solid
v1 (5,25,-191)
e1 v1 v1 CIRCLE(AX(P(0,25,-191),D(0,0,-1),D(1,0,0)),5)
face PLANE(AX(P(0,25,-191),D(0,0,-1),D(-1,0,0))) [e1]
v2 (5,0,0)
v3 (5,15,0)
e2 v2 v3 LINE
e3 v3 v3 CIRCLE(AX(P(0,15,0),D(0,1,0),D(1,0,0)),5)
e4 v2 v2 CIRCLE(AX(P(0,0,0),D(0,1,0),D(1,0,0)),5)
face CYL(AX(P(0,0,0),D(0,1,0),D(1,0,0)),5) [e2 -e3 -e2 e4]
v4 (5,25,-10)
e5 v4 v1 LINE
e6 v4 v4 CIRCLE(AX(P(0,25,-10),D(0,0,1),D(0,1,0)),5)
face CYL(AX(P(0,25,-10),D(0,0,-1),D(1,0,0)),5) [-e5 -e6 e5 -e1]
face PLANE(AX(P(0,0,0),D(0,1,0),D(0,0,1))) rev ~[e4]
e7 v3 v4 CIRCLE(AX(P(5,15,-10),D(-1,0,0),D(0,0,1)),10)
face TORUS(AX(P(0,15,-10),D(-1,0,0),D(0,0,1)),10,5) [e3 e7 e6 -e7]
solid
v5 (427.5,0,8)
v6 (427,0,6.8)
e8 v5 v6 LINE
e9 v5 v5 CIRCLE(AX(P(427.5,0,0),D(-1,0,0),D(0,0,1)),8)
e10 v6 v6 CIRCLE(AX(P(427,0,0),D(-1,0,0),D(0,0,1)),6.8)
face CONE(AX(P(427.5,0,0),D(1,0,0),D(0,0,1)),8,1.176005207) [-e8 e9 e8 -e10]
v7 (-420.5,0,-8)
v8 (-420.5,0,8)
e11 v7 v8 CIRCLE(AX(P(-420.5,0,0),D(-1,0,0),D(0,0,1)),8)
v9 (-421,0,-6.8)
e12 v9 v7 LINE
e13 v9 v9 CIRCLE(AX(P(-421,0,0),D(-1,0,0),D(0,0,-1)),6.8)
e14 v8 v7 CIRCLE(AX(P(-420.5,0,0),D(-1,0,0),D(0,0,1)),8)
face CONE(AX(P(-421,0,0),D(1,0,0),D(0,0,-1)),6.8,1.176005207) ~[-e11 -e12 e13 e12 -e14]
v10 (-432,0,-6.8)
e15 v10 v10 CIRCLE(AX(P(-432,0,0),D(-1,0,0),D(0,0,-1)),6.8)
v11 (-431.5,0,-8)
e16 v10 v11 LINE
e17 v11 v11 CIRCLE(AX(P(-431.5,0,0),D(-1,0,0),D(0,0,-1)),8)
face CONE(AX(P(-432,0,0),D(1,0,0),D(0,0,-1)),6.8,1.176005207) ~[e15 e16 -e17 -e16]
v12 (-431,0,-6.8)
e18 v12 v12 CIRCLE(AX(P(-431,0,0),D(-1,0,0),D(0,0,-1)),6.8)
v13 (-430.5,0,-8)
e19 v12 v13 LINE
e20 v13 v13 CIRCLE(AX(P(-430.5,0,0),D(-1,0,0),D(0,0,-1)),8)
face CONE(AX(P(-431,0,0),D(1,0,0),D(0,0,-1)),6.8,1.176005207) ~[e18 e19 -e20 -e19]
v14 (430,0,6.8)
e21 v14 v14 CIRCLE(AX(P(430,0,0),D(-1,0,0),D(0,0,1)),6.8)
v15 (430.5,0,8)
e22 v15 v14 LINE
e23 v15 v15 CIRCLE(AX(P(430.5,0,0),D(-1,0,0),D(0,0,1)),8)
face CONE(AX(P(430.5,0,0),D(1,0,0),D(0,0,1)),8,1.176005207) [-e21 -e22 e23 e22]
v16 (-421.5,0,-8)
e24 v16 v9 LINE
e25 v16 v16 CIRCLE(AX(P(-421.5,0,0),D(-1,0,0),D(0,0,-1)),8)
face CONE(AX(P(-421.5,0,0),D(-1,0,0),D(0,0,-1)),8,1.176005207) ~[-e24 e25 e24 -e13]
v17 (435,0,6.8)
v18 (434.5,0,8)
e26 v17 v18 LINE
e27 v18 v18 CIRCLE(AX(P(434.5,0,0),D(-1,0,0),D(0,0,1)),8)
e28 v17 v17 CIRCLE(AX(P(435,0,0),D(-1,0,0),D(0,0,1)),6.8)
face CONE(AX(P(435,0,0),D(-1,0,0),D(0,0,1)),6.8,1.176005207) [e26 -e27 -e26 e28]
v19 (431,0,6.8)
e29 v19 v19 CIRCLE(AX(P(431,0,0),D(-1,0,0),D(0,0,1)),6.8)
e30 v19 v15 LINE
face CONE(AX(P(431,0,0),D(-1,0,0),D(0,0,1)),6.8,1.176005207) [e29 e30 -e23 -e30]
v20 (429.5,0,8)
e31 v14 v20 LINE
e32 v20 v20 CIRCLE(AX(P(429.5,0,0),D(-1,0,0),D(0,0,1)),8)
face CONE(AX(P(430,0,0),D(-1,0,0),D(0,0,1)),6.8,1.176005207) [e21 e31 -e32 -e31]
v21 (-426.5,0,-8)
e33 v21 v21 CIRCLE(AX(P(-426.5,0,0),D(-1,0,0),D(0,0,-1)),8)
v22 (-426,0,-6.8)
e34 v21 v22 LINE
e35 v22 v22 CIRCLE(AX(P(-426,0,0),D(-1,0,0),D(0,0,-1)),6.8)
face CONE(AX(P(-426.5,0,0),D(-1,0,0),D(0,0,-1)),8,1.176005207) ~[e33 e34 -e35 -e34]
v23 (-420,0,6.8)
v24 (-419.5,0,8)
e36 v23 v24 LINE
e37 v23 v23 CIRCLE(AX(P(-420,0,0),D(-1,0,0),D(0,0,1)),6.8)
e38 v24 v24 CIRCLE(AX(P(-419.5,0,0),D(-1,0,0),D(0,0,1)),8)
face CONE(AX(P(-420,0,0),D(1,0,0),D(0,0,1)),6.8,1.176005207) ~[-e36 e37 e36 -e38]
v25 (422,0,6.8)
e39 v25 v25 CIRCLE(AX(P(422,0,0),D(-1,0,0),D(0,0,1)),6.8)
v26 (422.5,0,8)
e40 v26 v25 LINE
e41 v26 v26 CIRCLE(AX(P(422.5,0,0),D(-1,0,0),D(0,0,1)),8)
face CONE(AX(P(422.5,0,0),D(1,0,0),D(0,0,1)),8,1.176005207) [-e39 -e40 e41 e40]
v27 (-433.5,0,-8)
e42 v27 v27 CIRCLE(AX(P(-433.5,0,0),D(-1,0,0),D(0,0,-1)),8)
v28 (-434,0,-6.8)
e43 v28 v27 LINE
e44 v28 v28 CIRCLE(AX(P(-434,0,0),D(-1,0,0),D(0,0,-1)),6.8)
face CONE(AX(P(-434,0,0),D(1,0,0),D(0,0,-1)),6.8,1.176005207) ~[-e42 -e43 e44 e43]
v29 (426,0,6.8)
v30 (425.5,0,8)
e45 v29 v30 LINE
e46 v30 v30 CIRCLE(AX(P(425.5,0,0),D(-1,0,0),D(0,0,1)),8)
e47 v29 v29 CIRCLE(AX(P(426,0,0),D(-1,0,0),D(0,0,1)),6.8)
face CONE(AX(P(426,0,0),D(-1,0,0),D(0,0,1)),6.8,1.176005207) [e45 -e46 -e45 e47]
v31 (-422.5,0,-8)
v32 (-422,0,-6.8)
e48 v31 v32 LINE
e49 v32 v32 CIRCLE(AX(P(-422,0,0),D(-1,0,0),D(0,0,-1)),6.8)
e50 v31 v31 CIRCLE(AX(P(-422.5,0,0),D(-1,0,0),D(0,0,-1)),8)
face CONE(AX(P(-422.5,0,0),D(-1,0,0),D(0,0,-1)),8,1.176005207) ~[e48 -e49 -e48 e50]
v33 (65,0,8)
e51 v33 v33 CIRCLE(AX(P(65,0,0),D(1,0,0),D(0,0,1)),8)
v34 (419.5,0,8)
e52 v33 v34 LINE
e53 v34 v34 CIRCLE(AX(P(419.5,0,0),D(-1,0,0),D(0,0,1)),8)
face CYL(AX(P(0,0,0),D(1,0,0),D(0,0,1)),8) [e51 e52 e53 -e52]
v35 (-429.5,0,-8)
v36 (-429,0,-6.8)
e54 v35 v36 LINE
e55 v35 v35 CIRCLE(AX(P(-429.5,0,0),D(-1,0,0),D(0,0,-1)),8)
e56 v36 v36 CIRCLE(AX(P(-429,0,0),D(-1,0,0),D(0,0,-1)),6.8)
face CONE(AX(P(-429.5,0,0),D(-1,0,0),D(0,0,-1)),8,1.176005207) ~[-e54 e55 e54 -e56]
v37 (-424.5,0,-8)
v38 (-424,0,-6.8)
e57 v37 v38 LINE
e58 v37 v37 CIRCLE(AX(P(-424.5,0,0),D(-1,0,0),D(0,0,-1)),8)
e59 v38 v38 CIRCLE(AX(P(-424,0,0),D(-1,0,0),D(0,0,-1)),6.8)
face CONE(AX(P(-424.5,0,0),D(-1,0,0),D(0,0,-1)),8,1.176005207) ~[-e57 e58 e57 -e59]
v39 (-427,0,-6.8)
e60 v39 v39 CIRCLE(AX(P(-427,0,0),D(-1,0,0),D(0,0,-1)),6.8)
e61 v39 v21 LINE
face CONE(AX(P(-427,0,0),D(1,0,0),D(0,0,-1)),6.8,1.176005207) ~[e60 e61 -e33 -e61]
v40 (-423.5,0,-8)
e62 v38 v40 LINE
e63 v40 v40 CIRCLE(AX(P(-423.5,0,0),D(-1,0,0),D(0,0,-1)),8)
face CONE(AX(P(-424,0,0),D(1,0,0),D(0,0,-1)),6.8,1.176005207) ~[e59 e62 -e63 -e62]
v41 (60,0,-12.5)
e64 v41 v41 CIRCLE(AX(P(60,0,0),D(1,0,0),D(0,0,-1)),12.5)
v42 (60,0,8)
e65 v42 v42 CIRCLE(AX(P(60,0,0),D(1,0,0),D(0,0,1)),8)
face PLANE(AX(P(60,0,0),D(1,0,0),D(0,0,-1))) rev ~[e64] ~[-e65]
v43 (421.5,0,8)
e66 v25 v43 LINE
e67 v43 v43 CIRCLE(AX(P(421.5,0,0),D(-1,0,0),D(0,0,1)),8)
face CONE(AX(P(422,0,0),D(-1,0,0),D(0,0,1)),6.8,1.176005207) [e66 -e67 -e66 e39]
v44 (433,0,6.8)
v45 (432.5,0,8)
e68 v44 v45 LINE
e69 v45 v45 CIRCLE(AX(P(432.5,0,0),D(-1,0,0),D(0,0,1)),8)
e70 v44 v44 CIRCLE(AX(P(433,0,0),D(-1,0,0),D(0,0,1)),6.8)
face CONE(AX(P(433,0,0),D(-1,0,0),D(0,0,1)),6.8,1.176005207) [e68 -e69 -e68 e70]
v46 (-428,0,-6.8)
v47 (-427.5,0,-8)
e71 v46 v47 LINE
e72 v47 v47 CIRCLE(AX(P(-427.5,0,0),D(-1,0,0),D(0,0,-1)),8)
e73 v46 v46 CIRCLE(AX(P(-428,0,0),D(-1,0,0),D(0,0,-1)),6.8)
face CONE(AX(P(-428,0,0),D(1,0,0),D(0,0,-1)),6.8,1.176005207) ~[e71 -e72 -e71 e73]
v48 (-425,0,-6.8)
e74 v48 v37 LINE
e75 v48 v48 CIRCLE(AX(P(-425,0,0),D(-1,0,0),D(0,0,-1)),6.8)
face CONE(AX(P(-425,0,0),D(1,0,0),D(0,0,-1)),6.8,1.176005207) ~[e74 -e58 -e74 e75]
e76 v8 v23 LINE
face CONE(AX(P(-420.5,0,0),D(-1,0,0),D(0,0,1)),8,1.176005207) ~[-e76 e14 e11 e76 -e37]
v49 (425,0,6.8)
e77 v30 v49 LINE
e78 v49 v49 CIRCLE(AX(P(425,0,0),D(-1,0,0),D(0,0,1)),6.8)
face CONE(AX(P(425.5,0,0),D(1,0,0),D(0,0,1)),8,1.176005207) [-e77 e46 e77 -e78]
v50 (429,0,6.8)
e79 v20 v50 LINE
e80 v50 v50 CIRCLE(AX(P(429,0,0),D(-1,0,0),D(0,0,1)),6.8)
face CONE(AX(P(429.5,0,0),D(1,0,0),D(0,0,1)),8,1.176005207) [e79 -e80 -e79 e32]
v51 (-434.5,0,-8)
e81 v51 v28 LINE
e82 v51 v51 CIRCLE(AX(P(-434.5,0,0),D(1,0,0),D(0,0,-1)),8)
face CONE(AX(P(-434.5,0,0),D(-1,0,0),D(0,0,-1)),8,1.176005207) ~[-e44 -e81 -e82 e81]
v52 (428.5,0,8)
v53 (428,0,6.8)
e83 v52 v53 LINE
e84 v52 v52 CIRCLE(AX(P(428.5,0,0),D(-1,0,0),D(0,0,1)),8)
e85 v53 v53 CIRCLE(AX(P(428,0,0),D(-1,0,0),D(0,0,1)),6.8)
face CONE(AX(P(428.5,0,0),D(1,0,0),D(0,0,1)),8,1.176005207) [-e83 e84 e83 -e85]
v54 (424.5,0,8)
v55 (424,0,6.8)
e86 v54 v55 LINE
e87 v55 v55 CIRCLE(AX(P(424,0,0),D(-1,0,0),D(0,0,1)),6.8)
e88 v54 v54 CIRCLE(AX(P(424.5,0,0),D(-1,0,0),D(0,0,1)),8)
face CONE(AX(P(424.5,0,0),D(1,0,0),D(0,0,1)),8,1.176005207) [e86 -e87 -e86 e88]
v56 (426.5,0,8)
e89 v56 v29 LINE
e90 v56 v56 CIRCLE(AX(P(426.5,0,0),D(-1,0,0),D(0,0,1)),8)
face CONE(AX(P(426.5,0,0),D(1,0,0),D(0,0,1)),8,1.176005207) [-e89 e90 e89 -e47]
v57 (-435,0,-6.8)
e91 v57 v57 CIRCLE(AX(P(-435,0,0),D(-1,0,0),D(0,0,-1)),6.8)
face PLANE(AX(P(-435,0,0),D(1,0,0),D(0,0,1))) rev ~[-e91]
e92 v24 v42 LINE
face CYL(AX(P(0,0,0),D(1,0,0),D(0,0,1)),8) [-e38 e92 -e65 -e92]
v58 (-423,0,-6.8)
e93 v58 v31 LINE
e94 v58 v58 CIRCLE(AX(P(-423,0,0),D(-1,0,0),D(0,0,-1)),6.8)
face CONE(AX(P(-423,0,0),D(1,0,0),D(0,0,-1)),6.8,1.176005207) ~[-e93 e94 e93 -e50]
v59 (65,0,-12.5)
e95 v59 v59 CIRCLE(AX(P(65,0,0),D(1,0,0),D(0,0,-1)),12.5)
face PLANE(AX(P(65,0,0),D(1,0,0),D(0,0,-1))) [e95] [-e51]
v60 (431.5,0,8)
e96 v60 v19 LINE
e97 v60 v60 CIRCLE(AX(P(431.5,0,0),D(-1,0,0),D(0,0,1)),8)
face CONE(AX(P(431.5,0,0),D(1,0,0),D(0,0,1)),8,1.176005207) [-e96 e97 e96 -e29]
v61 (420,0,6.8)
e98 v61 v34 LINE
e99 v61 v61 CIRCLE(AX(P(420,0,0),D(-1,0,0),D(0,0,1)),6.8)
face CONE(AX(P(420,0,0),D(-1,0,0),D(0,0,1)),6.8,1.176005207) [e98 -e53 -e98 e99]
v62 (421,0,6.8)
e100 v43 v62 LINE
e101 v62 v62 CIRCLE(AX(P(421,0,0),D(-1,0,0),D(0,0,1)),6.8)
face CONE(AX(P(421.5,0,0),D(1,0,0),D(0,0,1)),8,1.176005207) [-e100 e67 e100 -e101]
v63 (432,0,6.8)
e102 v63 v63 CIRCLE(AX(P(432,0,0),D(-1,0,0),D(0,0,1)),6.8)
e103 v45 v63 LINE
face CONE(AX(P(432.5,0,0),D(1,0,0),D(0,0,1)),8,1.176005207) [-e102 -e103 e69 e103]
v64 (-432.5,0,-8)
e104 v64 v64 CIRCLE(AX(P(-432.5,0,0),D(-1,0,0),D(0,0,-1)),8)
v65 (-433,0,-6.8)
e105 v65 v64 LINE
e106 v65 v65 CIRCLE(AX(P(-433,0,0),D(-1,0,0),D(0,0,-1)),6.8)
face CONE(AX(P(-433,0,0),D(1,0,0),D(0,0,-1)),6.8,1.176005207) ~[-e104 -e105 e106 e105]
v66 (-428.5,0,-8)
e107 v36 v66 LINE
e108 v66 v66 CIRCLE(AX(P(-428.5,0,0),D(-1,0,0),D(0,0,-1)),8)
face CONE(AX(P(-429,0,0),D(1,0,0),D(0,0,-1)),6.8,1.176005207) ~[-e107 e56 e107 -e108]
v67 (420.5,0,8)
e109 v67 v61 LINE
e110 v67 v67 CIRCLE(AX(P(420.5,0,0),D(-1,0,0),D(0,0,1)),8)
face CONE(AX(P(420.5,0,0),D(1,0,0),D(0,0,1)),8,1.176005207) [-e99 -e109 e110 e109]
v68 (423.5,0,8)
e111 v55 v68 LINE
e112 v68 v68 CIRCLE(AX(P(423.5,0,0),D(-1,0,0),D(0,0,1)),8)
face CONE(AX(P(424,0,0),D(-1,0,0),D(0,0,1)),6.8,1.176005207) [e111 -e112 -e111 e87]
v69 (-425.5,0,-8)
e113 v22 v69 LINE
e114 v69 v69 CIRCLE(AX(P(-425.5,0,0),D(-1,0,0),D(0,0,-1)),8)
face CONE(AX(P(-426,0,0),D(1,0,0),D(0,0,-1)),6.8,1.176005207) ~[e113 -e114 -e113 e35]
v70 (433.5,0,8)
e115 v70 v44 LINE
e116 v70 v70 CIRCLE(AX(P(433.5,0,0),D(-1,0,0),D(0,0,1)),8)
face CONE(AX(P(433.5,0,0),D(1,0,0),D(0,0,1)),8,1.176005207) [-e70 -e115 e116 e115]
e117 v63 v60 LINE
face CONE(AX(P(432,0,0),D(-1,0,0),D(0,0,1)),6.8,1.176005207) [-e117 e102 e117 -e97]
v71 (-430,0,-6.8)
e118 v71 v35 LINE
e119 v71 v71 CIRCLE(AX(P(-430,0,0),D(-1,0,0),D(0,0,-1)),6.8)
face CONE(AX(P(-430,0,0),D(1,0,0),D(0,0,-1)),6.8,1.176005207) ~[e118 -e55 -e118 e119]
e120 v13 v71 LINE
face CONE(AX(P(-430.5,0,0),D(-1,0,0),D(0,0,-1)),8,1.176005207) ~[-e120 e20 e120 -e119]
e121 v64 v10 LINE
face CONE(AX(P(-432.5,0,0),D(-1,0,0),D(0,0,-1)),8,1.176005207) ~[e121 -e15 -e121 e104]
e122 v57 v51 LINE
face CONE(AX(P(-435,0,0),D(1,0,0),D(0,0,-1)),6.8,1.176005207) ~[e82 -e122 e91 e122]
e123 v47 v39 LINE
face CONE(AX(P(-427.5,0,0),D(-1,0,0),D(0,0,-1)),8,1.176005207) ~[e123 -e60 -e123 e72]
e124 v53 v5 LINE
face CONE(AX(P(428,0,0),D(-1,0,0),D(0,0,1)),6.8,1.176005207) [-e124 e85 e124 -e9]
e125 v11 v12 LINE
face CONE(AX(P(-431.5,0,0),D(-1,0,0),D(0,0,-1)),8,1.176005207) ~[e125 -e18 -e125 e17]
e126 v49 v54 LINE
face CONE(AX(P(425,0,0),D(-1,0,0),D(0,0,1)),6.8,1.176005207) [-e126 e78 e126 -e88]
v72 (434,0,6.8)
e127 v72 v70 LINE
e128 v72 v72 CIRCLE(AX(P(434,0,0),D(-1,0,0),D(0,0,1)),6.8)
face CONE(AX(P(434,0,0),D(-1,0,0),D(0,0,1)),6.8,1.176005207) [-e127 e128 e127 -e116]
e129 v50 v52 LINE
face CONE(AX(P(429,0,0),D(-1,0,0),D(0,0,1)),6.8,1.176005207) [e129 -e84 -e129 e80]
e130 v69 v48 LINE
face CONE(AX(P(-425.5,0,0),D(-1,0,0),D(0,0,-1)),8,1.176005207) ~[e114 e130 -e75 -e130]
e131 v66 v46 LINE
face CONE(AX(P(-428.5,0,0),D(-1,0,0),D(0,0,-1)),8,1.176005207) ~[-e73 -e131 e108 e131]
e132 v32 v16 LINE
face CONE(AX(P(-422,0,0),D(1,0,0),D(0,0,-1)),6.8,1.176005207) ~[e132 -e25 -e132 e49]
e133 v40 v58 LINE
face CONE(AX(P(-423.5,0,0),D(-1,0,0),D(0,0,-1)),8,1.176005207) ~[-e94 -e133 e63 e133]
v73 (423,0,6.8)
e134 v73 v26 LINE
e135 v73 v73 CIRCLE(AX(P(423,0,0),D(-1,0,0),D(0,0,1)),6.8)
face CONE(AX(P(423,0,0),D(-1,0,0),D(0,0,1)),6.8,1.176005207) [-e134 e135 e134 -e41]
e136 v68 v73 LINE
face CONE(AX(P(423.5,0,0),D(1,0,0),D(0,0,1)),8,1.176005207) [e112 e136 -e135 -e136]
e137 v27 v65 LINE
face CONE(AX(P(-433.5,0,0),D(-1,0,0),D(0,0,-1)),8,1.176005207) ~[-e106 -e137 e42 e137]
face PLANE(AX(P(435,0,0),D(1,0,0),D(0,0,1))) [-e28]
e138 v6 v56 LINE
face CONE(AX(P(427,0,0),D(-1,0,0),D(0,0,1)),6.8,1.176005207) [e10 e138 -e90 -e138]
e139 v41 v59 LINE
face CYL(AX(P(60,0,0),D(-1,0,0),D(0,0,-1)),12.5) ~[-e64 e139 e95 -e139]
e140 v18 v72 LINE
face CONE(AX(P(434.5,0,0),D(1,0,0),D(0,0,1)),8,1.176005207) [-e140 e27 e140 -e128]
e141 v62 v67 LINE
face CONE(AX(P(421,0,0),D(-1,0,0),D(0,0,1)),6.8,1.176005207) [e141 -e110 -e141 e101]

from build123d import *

# Parameters (mm, degrees)
SKETCH_3_R             = 5
SKETCH_4_R             = 8
EXTRUDE_2_DEPTH        = 435
PATTERN_LINEAR_1_COUNT = 16
PATTERN_LINEAR_1_PITCH = 1
SKETCH_8_R             = 12.5
EXTRUDE_3_DEPTH        = 5


with BuildPart() as part:
    # 扫描1: sweep along a path in 草图2
    with BuildLine(Plane(origin=(0, 0, 0), x_dir=(0, 0, -1), z_dir=(1, 0, 0))) as sweep_1_path:
        Line((0, 0), (0, 15))
        ThreePointArc((0, 15), (2.928932188, 22.071067812), (10, 25))
        Line((10, 25), (191, 25))
    # 草图3 → 扫描1 (sweep)
    with BuildSketch(Plane(origin=(0, 0, 0), x_dir=(1, 0, 0), z_dir=(0, 1, 0))):
        Circle(SKETCH_3_R)
    sweep(path=sweep_1_path.line)


with BuildPart() as body_2:
    # 草图4 → 凸台-拉伸2 (new, symmetric)
    with BuildSketch(Plane(origin=(0, 0, 0), x_dir=(0, 0, -1), z_dir=(1, 0, 0))):
        with Locations(Location((0, 0, 0), (0, 0, 180))):
            Circle(SKETCH_4_R)
    extrude(amount=EXTRUDE_2_DEPTH, both=True)

    # 草图7 → 切除-旋转1 (revolve, cut)
    with BuildSketch(Plane(origin=(0, 0, 0), x_dir=(1, 0, 0), z_dir=(0, 1, 0)), mode=Mode.PRIVATE) as cut_revolve_1_sk:
        Polygon((420, 8), (420.5, 8), (420, 6.8), (419.5, 8), align=None)
    cut_revolve_1 = revolve(cut_revolve_1_sk.sketch.rotate(Axis((442.161138775, 0, 0), (-1, 0, 0)), 180), axis=Axis((442.161138775, 0, 0), (-1, 0, 0)), mode=Mode.SUBTRACT)

    # 阵列(线性)1: 切除-旋转1 ×16
    with Locations(*[(i * PATTERN_LINEAR_1_PITCH, 0, 0) for i in range(1, PATTERN_LINEAR_1_COUNT)]):
        add(cut_revolve_1, mode=Mode.SUBTRACT)

    # 镜向2: 切除-旋转1 across plane
    add(cut_revolve_1.mirror(Plane(origin=(0, 0, 0), x_dir=(0, 0, 1), z_dir=(1, 0, 0))), mode=Mode.SUBTRACT)

    # 镜向2 copy 1 sketch → 镜向2 copy 1 (revolve, cut)
    with BuildSketch(Plane(origin=(-1, 0, 0), x_dir=(-1, 0, 0), z_dir=(0, 1, 0))):
        Polygon((420, -8), (420.5, -8), (420, -6.8), (419.5, -8), align=None)
    revolve(axis=Axis((-443.161138775, 0, 0), (-1, 0, 0)), mode=Mode.SUBTRACT)

    # 镜向2 copy 2 sketch → 镜向2 copy 2 (revolve, cut)
    with BuildSketch(Plane(origin=(-2, 0, 0), x_dir=(-1, 0, 0), z_dir=(0, 1, 0))):
        Polygon((420, -8), (420.5, -8), (420, -6.8), (419.5, -8), align=None)
    revolve(axis=Axis((-444.161138775, 0, 0), (-1, 0, 0)), mode=Mode.SUBTRACT)

    # 镜向2 copy 3 sketch → 镜向2 copy 3 (revolve, cut)
    with BuildSketch(Plane(origin=(-3, 0, 0), x_dir=(-1, 0, 0), z_dir=(0, 1, 0))):
        Polygon((420, -8), (420.5, -8), (420, -6.8), (419.5, -8), align=None)
    revolve(axis=Axis((-445.161138775, 0, 0), (-1, 0, 0)), mode=Mode.SUBTRACT)

    # 镜向2 copy 4 sketch → 镜向2 copy 4 (revolve, cut)
    with BuildSketch(Plane(origin=(-4, 0, 0), x_dir=(-1, 0, 0), z_dir=(0, 1, 0))):
        Polygon((420, -8), (420.5, -8), (420, -6.8), (419.5, -8), align=None)
    revolve(axis=Axis((-446.161138775, 0, 0), (-1, 0, 0)), mode=Mode.SUBTRACT)

    # 镜向2 copy 5 sketch → 镜向2 copy 5 (revolve, cut)
    with BuildSketch(Plane(origin=(-5, 0, 0), x_dir=(-1, 0, 0), z_dir=(0, 1, 0))):
        Polygon((420, -8), (420.5, -8), (420, -6.8), (419.5, -8), align=None)
    revolve(axis=Axis((-447.161138775, 0, 0), (-1, 0, 0)), mode=Mode.SUBTRACT)

    # 镜向2 copy 6 sketch → 镜向2 copy 6 (revolve, cut)
    with BuildSketch(Plane(origin=(-6, 0, 0), x_dir=(-1, 0, 0), z_dir=(0, 1, 0))):
        Polygon((420, -8), (420.5, -8), (420, -6.8), (419.5, -8), align=None)
    revolve(axis=Axis((-448.161138775, 0, 0), (-1, 0, 0)), mode=Mode.SUBTRACT)

    # 镜向2 copy 7 sketch → 镜向2 copy 7 (revolve, cut)
    with BuildSketch(Plane(origin=(-7, 0, 0), x_dir=(-1, 0, 0), z_dir=(0, 1, 0))):
        Polygon((420, -8), (420.5, -8), (420, -6.8), (419.5, -8), align=None)
    revolve(axis=Axis((-449.161138775, 0, 0), (-1, 0, 0)), mode=Mode.SUBTRACT)

    # 镜向2 copy 8 sketch → 镜向2 copy 8 (revolve, cut)
    with BuildSketch(Plane(origin=(-8, 0, 0), x_dir=(-1, 0, 0), z_dir=(0, 1, 0))):
        Polygon((420, -8), (420.5, -8), (420, -6.8), (419.5, -8), align=None)
    revolve(axis=Axis((-450.161138775, 0, 0), (-1, 0, 0)), mode=Mode.SUBTRACT)

    # 镜向2 copy 9 sketch → 镜向2 copy 9 (revolve, cut)
    with BuildSketch(Plane(origin=(-9, 0, 0), x_dir=(-1, 0, 0), z_dir=(0, 1, 0))):
        Polygon((420, -8), (420.5, -8), (420, -6.8), (419.5, -8), align=None)
    revolve(axis=Axis((-451.161138775, 0, 0), (-1, 0, 0)), mode=Mode.SUBTRACT)

    # 镜向2 copy 10 sketch → 镜向2 copy 10 (revolve, cut)
    with BuildSketch(Plane(origin=(-10, 0, 0), x_dir=(-1, 0, 0), z_dir=(0, 1, 0))):
        Polygon((420, -8), (420.5, -8), (420, -6.8), (419.5, -8), align=None)
    revolve(axis=Axis((-452.161138775, 0, 0), (-1, 0, 0)), mode=Mode.SUBTRACT)

    # 镜向2 copy 11 sketch → 镜向2 copy 11 (revolve, cut)
    with BuildSketch(Plane(origin=(-11, 0, 0), x_dir=(-1, 0, 0), z_dir=(0, 1, 0))):
        Polygon((420, -8), (420.5, -8), (420, -6.8), (419.5, -8), align=None)
    revolve(axis=Axis((-453.161138775, 0, 0), (-1, 0, 0)), mode=Mode.SUBTRACT)

    # 镜向2 copy 12 sketch → 镜向2 copy 12 (revolve, cut)
    with BuildSketch(Plane(origin=(-12, 0, 0), x_dir=(-1, 0, 0), z_dir=(0, 1, 0))):
        Polygon((420, -8), (420.5, -8), (420, -6.8), (419.5, -8), align=None)
    revolve(axis=Axis((-454.161138775, 0, 0), (-1, 0, 0)), mode=Mode.SUBTRACT)

    # 镜向2 copy 13 sketch → 镜向2 copy 13 (revolve, cut)
    with BuildSketch(Plane(origin=(-13, 0, 0), x_dir=(-1, 0, 0), z_dir=(0, 1, 0))):
        Polygon((420, -8), (420.5, -8), (420, -6.8), (419.5, -8), align=None)
    revolve(axis=Axis((-455.161138775, 0, 0), (-1, 0, 0)), mode=Mode.SUBTRACT)

    # 镜向2 copy 14 sketch → 镜向2 copy 14 (revolve, cut)
    with BuildSketch(Plane(origin=(-14, 0, 0), x_dir=(-1, 0, 0), z_dir=(0, 1, 0))):
        Polygon((420, -8), (420.5, -8), (420, -6.8), (419.5, -8), align=None)
    revolve(axis=Axis((-456.161138775, 0, 0), (-1, 0, 0)), mode=Mode.SUBTRACT)

    # 镜向2 copy 15 sketch → 镜向2 copy 15 (revolve, cut)
    with BuildSketch(Plane(origin=(-15, 0, 0), x_dir=(-1, 0, 0), z_dir=(0, 1, 0))):
        Polygon((420, -8), (420.5, -8), (420, -6.8), (419.5, -8), align=None)
    revolve(axis=Axis((-457.161138775, 0, 0), (-1, 0, 0)), mode=Mode.SUBTRACT)

    # 草图8 → 凸台-拉伸3 (add)
    with BuildSketch(Plane(origin=(60, 0, 0), x_dir=(0, 0, -1), z_dir=(1, 0, 0))):
        Circle(SKETCH_8_R)
    extrude(amount=EXTRUDE_3_DEPTH)


solid = Compound([part.part, body_2.part])
